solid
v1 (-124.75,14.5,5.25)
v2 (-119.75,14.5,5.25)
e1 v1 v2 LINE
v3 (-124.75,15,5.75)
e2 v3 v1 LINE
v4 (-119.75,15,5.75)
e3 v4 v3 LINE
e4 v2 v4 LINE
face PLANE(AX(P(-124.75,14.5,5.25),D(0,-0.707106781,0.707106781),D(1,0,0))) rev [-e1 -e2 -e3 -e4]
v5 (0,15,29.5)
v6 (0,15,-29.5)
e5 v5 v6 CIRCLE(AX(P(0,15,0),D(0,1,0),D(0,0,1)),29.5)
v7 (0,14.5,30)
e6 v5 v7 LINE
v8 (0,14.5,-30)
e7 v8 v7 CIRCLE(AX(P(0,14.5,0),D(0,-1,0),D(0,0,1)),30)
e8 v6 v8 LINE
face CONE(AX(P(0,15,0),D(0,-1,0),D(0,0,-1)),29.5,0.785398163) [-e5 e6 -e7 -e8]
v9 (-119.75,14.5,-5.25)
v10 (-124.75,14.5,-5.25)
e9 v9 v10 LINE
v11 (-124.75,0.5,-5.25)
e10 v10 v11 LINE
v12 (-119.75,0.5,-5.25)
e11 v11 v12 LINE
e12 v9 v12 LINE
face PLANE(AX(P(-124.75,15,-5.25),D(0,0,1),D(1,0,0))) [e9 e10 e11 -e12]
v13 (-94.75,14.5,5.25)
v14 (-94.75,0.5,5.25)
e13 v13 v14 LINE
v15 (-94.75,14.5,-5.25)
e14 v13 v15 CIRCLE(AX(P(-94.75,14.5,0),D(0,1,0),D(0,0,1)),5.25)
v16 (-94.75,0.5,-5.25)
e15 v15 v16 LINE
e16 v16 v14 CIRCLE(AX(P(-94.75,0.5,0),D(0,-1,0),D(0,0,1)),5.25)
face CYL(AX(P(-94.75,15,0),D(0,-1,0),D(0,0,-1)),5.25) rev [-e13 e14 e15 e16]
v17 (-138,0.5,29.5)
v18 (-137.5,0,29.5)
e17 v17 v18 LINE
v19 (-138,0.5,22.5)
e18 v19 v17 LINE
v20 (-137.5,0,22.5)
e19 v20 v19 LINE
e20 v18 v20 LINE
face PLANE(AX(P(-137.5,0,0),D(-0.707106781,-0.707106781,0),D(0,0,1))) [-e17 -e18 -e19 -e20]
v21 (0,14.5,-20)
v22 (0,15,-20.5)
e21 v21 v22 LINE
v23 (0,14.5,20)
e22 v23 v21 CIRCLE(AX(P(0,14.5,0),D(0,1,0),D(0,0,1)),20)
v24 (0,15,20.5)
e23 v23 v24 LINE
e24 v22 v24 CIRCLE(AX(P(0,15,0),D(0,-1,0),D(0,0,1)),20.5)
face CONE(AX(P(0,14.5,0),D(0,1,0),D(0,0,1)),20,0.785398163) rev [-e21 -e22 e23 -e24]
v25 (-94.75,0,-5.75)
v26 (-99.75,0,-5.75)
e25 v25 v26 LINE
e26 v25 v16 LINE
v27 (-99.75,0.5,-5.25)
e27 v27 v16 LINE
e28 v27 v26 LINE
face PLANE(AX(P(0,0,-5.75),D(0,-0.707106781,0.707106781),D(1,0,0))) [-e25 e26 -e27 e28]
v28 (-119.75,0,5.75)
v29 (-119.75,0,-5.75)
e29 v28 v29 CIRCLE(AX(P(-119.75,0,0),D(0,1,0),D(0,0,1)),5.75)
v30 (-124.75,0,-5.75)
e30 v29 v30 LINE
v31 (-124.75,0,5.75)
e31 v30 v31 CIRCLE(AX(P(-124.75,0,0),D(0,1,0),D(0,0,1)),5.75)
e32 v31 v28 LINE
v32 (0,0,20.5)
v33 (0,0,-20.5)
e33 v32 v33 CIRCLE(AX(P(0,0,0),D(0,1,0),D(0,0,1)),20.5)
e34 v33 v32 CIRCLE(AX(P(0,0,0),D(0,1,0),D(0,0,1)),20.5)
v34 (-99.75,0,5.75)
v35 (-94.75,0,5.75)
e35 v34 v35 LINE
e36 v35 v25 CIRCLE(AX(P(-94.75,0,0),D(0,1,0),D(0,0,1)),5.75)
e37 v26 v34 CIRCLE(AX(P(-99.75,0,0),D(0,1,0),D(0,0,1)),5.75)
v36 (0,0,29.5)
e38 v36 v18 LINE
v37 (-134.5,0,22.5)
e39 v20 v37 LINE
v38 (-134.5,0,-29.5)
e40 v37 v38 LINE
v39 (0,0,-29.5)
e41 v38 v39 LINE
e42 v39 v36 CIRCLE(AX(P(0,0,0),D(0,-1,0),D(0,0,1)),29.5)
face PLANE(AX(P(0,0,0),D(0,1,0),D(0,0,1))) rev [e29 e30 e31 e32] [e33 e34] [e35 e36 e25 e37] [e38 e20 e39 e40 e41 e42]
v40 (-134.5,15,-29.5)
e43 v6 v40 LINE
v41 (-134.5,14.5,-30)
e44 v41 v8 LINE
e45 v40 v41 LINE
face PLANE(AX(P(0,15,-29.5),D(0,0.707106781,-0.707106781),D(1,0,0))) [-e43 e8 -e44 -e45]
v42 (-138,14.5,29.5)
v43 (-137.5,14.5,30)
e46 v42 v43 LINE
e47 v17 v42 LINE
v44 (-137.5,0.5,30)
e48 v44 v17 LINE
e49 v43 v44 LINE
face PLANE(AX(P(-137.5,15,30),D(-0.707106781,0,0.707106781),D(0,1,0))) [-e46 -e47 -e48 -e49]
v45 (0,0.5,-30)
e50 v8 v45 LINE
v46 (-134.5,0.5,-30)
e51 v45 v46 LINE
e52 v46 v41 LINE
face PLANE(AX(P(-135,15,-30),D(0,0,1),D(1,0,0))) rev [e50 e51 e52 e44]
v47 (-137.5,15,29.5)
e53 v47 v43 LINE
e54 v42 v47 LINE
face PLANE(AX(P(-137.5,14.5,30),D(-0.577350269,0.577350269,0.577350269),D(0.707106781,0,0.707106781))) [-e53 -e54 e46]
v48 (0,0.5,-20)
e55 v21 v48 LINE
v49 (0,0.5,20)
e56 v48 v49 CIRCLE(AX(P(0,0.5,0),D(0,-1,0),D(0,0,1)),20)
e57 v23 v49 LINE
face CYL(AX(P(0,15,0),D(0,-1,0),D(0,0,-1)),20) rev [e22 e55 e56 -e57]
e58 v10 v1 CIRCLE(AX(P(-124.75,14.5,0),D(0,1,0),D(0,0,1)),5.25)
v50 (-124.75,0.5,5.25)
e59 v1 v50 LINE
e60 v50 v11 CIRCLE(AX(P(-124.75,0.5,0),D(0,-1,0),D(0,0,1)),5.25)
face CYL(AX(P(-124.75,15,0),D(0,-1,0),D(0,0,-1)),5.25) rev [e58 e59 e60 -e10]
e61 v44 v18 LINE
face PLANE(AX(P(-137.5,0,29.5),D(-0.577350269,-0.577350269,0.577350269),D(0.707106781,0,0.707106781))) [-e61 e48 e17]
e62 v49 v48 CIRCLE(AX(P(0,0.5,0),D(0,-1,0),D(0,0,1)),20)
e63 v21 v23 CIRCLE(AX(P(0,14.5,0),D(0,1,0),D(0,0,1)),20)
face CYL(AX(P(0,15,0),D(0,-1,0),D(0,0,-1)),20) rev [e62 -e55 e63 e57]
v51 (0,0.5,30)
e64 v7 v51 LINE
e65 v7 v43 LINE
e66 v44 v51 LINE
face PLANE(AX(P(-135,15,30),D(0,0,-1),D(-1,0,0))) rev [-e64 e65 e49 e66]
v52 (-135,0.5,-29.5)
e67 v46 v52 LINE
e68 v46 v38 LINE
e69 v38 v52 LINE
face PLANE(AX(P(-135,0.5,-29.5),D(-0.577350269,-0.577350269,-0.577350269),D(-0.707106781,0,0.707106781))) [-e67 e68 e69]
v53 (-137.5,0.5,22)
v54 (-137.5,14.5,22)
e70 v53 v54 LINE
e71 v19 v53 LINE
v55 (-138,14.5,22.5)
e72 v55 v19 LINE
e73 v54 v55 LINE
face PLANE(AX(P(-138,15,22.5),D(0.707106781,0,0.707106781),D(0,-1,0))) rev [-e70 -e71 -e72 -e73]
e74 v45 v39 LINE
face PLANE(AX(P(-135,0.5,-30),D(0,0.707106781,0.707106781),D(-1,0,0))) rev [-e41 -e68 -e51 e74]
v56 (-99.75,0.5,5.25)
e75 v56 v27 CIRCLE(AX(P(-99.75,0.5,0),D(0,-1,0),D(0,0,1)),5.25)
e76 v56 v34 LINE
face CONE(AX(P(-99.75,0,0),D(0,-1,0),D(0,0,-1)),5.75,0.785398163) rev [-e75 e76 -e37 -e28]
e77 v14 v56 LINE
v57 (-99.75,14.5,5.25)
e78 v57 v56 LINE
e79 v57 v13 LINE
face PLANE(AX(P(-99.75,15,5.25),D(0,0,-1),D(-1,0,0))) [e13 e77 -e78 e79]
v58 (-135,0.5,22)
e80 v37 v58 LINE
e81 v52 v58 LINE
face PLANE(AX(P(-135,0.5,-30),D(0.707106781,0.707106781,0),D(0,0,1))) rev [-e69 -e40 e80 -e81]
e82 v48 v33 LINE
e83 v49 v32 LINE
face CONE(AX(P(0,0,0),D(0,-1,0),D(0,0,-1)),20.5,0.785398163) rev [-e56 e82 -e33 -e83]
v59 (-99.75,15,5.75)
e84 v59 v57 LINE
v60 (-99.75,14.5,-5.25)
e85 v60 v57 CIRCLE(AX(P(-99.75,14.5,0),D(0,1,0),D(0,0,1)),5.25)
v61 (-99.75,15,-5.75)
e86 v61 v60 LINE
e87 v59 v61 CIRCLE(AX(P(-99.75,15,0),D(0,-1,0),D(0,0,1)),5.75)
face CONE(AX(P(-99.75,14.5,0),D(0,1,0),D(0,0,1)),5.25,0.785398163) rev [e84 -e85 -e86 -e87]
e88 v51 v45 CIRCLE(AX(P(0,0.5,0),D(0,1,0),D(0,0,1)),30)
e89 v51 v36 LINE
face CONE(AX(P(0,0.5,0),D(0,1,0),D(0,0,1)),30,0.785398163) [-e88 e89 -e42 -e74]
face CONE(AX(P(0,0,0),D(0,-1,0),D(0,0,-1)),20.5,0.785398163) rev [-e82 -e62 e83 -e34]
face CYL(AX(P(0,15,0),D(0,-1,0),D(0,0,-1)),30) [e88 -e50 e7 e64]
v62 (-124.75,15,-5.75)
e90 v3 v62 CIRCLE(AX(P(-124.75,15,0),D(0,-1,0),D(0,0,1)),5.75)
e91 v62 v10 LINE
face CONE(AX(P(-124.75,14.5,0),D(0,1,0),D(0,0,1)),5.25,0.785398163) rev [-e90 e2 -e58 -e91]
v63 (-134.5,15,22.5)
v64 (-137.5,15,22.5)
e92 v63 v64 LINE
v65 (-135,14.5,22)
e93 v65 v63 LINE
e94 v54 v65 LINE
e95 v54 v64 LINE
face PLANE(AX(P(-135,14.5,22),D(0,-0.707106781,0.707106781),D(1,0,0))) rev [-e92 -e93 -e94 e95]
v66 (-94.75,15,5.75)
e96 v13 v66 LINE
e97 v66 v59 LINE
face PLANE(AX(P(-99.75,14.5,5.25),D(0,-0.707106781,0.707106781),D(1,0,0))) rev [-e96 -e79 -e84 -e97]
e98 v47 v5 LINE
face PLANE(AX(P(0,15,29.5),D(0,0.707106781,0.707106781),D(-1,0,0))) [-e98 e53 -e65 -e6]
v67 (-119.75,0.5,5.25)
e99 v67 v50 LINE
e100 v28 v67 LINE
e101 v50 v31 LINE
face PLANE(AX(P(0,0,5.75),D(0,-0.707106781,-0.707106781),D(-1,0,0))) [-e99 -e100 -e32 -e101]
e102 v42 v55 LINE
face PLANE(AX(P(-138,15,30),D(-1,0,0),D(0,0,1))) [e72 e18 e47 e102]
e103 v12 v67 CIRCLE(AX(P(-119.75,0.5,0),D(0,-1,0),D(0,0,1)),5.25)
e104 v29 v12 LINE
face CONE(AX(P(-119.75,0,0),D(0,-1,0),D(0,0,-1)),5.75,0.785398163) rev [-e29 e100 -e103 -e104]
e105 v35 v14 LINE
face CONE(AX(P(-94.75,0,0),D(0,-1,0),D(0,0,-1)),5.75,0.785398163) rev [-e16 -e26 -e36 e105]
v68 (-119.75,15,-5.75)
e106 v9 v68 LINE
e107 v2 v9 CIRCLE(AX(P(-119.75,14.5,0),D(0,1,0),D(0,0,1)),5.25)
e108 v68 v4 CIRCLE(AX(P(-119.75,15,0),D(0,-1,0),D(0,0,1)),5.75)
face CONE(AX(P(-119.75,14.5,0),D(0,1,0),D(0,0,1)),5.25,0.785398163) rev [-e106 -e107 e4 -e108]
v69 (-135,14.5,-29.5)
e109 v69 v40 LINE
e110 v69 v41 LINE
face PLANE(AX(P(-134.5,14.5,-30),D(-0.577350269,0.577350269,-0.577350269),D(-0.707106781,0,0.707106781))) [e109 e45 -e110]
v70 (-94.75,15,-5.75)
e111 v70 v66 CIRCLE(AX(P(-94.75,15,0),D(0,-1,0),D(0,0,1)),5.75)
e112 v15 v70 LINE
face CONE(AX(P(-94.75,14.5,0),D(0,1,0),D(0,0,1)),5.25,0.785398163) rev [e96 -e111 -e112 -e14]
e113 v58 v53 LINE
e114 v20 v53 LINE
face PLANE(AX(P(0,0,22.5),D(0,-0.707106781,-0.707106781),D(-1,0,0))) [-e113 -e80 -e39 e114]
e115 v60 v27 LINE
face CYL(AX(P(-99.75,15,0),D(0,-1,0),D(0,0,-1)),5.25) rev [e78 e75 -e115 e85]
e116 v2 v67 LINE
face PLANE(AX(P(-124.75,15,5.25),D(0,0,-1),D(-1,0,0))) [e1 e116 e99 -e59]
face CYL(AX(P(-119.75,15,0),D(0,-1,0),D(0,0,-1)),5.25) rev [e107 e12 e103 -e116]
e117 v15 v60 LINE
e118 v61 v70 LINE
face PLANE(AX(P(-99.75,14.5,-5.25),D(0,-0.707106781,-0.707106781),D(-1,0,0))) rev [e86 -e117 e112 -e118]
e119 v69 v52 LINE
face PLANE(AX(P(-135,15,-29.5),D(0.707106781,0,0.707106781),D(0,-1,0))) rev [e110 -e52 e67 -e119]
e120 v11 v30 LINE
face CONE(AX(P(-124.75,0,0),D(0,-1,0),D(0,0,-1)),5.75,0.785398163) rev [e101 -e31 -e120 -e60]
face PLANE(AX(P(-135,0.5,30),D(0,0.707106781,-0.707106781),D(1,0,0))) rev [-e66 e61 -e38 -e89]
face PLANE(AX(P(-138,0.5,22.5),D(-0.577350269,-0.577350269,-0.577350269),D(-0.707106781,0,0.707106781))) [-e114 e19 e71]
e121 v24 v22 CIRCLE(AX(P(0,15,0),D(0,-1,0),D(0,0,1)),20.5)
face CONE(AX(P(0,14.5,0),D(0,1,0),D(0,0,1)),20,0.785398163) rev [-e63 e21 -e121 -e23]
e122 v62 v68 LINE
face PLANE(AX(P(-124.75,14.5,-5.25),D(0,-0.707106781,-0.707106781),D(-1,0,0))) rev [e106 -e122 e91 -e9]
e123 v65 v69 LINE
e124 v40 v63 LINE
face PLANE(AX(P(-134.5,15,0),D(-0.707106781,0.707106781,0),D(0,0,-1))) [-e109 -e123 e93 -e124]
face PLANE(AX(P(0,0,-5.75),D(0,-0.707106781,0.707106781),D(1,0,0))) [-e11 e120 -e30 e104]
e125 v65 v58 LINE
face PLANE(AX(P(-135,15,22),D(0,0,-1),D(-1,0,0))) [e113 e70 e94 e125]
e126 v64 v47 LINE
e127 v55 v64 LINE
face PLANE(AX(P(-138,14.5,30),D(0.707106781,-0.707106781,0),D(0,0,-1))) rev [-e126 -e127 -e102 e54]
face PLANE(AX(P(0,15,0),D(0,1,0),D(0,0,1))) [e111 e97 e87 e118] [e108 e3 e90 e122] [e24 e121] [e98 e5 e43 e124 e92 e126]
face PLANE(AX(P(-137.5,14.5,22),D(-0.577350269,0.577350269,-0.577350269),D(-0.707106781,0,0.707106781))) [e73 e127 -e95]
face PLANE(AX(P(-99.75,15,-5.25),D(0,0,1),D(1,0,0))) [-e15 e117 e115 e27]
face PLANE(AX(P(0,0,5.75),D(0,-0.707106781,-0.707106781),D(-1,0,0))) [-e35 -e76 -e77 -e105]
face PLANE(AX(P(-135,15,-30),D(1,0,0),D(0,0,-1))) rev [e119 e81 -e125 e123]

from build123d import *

# Parameters (mm, degrees)
SKETCH_1_R      = 20
EXTRUDE_1_DEPTH = 15
SKETCH_3_W      = 3
SKETCH_3_H      = 8
EXTRUDE_3_DEPTH = 15
CHAMFER_2_SIZE  = 0.5


with BuildPart() as part:
    # 草图1 → 凸台-拉伸1 (new body)
    with BuildSketch(Plane(origin=(0, 0, 0), x_dir=(1, 0, 0), z_dir=(0, 1, 0))):
        with BuildLine():
            Line((-135, 30), (-135, -30))
            Line((-135, -30), (0, -30))
            ThreePointArc((0, -30), (30, 0), (0, 30))
            Line((0, 30), (-135, 30))
        make_face()
        with Locations(Location((0, 0, 0), (0, 0, 270))):
            Circle(SKETCH_1_R, mode=Mode.SUBTRACT)
        with BuildLine():
            Line((-124.75, 5.25), (-119.75, 5.25))
            ThreePointArc((-119.75, 5.25), (-114.5, 0), (-119.75, -5.25))
            Line((-119.75, -5.25), (-124.75, -5.25))
            ThreePointArc((-124.75, -5.25), (-130, 0), (-124.75, 5.25))
        make_face(mode=Mode.SUBTRACT)
        with BuildLine():
            Line((-99.75, 5.25), (-94.75, 5.25))
            ThreePointArc((-94.75, 5.25), (-89.5, 0), (-94.75, -5.25))
            Line((-94.75, -5.25), (-99.75, -5.25))
            ThreePointArc((-99.75, -5.25), (-105, 0), (-99.75, 5.25))
        make_face(mode=Mode.SUBTRACT)
    extrude(amount=EXTRUDE_1_DEPTH)

    # 草图3 → 凸台-拉伸3 (add, through all)
    with BuildSketch(Plane.XZ):
        with Locations((-136.5, 26)):
            Rectangle(SKETCH_3_W, SKETCH_3_H)
    extrude(amount=-EXTRUDE_3_DEPTH)

    # 倒角2
    chamfer_2_edges = [part.edges().sort_by_distance(p)[0] for p in [
        (-67.5, 15, -30),
        (0, 0, -20),
        (0, 15, -20),
        (-135, 15, -4),
        (-130, 0, 0),
        (-122.25, 0, 5.25),
        (-114.5, 0, 0),
        (-122.25, 0, -5.25),
        (-130, 15, 0),
        (-122.25, 15, 5.25),
        (-114.5, 15, 0),
        (-122.25, 15, -5.25),
        (-105, 0, 0),
        (-97.25, 0, 5.25),
        (-89.5, 0, 0),
        (-97.25, 0, -5.25),
        (-105, 15, 0),
        (-97.25, 15, 5.25),
        (-89.5, 15, 0),
        (-97.25, 15, -5.25),
        (-69, 15, 30),
        (-135, 0, -4),
        (-136.5, 15, 22),
        (-138, 15, 26),
        (-138, 7.5, 22),
        (-138, 7.5, 30),
        (-67.5, 0, -30),
        (-138, 0, 26),
        (-136.5, 0, 22),
        (30, 0, 0),
        (-69, 0, 30),
        (30, 15, 0),
        (-135, 7.5, -30),
    ]]
    chamfer(chamfer_2_edges, length=CHAMFER_2_SIZE)


solid = part.part
